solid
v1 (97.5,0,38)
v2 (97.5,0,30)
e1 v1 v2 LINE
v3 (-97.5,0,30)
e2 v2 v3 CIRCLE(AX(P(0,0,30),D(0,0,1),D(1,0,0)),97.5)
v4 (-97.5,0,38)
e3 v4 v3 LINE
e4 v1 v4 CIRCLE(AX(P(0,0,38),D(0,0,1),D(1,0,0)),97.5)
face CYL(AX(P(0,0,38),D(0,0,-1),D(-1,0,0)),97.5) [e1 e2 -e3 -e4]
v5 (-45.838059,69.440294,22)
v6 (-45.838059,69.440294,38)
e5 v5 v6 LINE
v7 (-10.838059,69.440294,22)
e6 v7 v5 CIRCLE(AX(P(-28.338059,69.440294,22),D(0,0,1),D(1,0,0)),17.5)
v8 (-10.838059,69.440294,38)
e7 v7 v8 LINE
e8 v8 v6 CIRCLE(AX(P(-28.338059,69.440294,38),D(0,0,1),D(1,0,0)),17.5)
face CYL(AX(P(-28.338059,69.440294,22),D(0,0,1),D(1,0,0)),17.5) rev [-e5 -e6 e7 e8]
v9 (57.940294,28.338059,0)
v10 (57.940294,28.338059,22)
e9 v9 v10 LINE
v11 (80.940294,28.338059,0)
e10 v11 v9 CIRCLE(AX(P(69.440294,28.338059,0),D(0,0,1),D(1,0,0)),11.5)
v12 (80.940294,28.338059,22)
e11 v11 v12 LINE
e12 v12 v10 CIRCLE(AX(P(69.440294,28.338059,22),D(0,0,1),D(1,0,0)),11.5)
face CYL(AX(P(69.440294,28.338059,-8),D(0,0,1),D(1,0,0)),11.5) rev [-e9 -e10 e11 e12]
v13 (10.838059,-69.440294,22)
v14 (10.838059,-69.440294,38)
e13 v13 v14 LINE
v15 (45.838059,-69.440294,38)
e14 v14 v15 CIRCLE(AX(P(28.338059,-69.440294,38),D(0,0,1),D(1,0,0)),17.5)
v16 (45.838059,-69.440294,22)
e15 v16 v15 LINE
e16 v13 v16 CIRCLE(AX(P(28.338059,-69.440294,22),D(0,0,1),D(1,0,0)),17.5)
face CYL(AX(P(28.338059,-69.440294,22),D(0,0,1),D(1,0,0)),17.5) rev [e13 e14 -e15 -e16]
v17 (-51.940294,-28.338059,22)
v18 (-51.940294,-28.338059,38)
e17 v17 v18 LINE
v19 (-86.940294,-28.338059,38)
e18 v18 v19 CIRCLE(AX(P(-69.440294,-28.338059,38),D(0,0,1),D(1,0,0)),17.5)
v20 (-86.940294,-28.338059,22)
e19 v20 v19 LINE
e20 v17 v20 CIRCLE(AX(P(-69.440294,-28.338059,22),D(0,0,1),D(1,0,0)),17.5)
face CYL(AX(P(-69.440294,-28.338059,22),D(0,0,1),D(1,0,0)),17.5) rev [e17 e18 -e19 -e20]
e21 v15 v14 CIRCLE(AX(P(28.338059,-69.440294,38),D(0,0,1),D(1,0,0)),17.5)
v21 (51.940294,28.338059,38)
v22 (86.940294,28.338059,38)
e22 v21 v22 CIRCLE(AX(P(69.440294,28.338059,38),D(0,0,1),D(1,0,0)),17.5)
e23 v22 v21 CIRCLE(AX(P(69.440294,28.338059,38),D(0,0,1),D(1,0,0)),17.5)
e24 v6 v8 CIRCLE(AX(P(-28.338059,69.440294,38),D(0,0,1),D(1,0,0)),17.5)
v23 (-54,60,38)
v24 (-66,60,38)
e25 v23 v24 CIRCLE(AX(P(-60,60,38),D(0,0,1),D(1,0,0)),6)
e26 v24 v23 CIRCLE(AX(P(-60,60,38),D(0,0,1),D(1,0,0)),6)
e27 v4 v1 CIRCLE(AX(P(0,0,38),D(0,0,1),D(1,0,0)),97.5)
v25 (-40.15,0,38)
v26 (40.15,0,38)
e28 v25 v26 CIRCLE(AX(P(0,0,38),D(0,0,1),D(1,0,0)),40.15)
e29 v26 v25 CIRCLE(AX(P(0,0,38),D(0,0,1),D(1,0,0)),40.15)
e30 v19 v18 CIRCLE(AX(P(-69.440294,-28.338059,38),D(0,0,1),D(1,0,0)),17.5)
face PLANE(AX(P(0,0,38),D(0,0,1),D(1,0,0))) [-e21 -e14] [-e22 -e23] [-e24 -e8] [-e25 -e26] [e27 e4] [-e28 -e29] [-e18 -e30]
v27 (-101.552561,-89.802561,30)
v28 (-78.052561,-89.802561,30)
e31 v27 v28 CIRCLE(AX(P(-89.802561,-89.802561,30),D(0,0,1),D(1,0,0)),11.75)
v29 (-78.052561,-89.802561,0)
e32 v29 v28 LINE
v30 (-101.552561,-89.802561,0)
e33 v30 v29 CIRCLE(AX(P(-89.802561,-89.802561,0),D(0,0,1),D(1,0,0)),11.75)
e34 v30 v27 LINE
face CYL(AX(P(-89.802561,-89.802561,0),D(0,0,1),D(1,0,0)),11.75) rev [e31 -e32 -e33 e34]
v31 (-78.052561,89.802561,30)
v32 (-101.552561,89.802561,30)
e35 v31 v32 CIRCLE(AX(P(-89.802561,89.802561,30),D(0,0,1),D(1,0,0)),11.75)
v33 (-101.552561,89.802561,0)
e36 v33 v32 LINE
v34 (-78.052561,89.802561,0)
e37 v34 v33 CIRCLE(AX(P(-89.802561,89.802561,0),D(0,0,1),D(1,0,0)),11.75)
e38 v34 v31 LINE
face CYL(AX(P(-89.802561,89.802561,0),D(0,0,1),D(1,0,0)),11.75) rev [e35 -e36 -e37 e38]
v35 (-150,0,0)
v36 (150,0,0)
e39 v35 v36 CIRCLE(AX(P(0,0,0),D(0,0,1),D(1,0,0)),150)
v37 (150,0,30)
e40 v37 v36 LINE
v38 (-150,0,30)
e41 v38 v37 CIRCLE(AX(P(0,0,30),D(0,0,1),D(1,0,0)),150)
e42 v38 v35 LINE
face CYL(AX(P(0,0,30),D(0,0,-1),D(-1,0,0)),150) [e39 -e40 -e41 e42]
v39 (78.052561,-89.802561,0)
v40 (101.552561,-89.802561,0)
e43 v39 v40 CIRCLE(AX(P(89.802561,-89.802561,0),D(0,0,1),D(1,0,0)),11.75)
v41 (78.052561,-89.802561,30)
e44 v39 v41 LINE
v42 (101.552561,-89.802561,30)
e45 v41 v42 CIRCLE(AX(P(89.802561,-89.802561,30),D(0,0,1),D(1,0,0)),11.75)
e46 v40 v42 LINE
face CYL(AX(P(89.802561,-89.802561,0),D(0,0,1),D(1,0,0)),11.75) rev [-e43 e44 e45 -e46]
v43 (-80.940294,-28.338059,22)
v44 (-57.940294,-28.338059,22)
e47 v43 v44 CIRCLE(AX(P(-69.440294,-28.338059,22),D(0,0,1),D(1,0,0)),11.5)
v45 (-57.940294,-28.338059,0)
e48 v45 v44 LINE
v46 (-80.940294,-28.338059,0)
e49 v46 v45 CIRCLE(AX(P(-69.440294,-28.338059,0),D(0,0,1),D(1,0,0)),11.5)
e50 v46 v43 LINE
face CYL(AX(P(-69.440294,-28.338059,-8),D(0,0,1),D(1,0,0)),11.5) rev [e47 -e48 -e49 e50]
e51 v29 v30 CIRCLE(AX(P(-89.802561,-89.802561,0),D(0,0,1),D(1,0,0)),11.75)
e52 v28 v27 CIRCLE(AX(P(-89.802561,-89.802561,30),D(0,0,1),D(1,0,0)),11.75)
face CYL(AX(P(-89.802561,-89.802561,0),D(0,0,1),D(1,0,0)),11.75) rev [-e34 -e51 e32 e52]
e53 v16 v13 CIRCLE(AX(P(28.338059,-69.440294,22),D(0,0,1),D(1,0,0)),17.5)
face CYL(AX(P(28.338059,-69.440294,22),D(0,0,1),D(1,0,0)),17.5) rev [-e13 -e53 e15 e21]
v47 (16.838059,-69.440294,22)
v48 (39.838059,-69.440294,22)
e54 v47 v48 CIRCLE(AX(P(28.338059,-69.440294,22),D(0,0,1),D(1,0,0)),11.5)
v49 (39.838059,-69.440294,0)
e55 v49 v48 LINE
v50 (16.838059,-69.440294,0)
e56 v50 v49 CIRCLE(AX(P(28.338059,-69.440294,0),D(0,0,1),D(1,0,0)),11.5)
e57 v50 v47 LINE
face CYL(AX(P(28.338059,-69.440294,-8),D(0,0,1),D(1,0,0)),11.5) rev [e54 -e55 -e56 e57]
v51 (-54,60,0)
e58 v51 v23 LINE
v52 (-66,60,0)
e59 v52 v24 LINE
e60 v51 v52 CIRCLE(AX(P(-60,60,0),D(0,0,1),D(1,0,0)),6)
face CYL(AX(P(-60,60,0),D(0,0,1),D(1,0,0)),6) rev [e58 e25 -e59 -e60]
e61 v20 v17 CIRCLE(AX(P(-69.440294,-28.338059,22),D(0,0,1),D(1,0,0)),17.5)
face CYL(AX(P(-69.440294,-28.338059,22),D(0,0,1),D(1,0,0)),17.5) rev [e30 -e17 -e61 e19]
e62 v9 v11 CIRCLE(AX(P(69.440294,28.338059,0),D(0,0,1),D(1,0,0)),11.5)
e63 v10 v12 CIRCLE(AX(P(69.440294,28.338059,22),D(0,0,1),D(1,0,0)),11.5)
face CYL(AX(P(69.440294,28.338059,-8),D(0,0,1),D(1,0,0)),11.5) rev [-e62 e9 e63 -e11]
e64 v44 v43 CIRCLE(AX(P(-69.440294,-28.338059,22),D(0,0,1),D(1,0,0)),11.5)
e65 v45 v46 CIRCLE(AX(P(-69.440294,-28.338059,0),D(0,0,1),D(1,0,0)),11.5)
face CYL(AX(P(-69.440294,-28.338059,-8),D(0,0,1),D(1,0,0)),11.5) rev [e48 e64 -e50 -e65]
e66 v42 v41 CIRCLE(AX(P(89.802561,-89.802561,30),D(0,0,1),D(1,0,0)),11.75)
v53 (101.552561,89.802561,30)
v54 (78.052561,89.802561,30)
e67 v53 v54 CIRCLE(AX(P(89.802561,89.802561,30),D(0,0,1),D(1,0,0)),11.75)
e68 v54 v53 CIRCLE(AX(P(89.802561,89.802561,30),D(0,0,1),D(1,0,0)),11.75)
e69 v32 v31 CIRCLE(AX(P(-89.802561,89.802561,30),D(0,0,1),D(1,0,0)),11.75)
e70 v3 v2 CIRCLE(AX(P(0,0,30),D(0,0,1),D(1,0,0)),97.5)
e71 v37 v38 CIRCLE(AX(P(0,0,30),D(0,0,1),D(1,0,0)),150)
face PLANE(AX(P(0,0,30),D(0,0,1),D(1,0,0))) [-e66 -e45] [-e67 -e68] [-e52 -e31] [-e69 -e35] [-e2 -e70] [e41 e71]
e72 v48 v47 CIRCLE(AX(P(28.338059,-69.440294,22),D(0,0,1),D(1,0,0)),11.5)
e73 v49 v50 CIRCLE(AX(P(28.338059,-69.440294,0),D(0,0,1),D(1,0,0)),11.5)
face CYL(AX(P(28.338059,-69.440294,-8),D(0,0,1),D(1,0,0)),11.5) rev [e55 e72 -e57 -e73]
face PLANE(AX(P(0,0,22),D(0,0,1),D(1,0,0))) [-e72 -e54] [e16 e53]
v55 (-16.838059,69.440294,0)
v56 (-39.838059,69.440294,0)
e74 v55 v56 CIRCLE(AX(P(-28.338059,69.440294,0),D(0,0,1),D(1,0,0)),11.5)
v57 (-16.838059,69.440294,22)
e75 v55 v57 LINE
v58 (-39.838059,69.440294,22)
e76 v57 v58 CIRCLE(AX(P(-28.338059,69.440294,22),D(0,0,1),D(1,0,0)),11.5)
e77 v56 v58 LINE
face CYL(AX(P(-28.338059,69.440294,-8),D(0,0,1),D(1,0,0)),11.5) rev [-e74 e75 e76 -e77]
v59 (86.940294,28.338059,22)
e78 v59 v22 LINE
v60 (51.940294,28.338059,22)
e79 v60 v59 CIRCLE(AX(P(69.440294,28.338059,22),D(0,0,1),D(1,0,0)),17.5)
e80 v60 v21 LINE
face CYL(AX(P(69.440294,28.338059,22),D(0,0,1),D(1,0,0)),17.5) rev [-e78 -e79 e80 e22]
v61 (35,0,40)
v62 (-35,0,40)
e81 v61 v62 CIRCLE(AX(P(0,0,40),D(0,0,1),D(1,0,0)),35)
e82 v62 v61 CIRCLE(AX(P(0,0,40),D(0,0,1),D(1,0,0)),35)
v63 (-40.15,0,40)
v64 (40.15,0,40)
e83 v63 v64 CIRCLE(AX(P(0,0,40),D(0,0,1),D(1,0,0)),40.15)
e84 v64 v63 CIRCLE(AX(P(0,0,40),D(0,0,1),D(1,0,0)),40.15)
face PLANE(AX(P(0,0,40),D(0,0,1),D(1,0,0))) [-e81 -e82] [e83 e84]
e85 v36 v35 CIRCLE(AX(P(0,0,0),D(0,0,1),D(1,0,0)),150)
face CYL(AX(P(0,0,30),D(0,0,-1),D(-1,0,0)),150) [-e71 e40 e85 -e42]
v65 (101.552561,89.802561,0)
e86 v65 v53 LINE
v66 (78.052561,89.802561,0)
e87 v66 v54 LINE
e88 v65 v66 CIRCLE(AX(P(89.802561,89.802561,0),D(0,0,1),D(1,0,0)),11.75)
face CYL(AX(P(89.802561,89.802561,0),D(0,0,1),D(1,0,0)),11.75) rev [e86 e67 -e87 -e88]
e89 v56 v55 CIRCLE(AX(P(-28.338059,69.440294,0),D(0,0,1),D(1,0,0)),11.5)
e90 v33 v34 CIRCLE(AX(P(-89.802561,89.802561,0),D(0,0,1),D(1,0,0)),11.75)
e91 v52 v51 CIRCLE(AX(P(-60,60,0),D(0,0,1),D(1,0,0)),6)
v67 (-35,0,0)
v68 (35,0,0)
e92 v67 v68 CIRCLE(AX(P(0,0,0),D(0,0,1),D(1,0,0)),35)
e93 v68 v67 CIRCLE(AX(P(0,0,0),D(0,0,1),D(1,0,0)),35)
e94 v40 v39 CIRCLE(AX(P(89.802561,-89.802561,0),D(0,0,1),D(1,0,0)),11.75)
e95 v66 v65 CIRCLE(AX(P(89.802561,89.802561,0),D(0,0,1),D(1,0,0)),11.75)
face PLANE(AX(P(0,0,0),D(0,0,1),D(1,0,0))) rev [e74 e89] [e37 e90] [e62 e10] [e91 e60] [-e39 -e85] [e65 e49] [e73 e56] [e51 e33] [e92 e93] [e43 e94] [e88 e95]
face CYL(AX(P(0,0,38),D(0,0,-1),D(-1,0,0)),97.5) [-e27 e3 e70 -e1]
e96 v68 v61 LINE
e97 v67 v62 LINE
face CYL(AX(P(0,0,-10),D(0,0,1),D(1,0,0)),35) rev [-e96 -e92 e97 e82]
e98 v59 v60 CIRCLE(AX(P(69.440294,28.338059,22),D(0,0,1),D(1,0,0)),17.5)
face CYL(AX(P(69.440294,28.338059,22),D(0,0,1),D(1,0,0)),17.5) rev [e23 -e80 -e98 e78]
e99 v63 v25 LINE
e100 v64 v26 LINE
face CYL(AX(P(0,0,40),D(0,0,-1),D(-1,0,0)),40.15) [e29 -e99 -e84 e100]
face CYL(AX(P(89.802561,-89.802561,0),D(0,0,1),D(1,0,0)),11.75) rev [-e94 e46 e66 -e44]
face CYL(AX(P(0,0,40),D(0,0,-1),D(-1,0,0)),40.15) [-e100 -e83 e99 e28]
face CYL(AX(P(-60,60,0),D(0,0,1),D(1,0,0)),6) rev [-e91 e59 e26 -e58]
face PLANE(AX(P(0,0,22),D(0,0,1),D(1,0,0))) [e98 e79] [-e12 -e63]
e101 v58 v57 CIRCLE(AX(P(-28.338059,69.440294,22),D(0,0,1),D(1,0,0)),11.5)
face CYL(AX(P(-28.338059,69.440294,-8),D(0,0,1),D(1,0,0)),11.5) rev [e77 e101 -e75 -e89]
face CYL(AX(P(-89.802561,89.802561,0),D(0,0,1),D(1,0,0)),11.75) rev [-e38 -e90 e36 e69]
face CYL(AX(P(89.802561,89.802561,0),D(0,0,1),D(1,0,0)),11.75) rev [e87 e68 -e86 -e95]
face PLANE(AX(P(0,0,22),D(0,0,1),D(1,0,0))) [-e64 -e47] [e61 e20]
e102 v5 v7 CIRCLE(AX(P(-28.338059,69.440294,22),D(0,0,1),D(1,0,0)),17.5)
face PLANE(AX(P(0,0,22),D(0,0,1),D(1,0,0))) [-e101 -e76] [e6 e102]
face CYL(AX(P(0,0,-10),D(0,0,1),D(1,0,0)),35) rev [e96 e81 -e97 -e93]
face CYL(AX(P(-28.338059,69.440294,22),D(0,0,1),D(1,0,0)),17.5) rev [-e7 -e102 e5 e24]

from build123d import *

# Parameters (mm, degrees)
FLANGE_DISC_PROFILE_R          = 150
FLANGE_DISC_300_DEPTH          = 30
RAISED_FACE_PROFILE_R          = 97.5
RAISED_FACE_195_DEPTH          = 8
HUB_SPIGOT_PROFILE_R           = 40.15
HUB_SPIGOT_80_3_DEPTH          = 2
THROUGH_HOLES_PROFILE_R        = 6
THROUGH_HOLES_PROFILE_R_2      = 11.75
THROUGH_HOLES_PCD254_DEPTH     = 40
COUNTERBORE_PROFILE_R          = 17.5
COUNTERBORES_4X_35_DEPTH       = 16
COUNTERBORED_HOLES_PROFILE_R   = 11.5
COUNTERBORED_HOLES_4X_23_DEPTH = 30
CENTRAL_BORE_PROFILE_R         = 35
CENTRAL_BORE_70_DEPTH          = 50


with BuildPart() as part:
    # Flange Disc Profile → Flange Disc Ø300 (new body)
    with BuildSketch(Plane.XY):
        Circle(FLANGE_DISC_PROFILE_R)
    extrude(amount=FLANGE_DISC_300_DEPTH)

    # Raised Face Profile → Raised Face Ø195 (add)
    with BuildSketch(Plane.XY.offset(30)):
        Circle(RAISED_FACE_PROFILE_R)
    extrude(amount=RAISED_FACE_195_DEPTH)

    # Hub Spigot Profile → Hub Spigot Ø80.3 (add)
    with BuildSketch(Plane.XY.offset(38)):
        Circle(HUB_SPIGOT_PROFILE_R)
    extrude(amount=HUB_SPIGOT_80_3_DEPTH)

    # Through Holes Profile → Through Holes PCD254 (cut)
    with BuildSketch(Plane.XY.offset(40)):
        with Locations((-60, 60)):
            Circle(THROUGH_HOLES_PROFILE_R)
        with Locations((89.802561211, 89.802561211)):
            Circle(THROUGH_HOLES_PROFILE_R_2)
        with Locations((89.802561211, -89.802561211)):
            Circle(THROUGH_HOLES_PROFILE_R_2)
        with Locations((-89.802561211, -89.802561211)):
            Circle(THROUGH_HOLES_PROFILE_R_2)
        with Locations((-89.802561211, 89.802561211)):
            Circle(THROUGH_HOLES_PROFILE_R_2)
    extrude(amount=-THROUGH_HOLES_PCD254_DEPTH, mode=Mode.SUBTRACT)

    # Counterbore Profile → Counterbores 4xØ35 (cut)
    with BuildSketch(Plane.XY.offset(38)):
        with Locations((-28.338059011, 69.440293861)):
            Circle(COUNTERBORE_PROFILE_R)
        with Locations((69.440293861, 28.338059011)):
            Circle(COUNTERBORE_PROFILE_R)
        with Locations((28.338059011, -69.440293861)):
            Circle(COUNTERBORE_PROFILE_R)
        with Locations((-69.440293861, -28.338059011)):
            Circle(COUNTERBORE_PROFILE_R)
    extrude(amount=-COUNTERBORES_4X_35_DEPTH, mode=Mode.SUBTRACT)

    # Counterbored Holes Profile → Counterbored Holes 4xØ23 (cut)
    with BuildSketch(Plane.XY.offset(22)):
        with Locations((-28.338059011, 69.440293861)):
            Circle(COUNTERBORED_HOLES_PROFILE_R)
        with Locations((69.440293861, 28.338059011)):
            Circle(COUNTERBORED_HOLES_PROFILE_R)
        with Locations((28.338059011, -69.440293861)):
            Circle(COUNTERBORED_HOLES_PROFILE_R)
        with Locations((-69.440293861, -28.338059011)):
            Circle(COUNTERBORED_HOLES_PROFILE_R)
    extrude(amount=-COUNTERBORED_HOLES_4X_23_DEPTH, mode=Mode.SUBTRACT)

    # Central Bore Profile → Central Bore Ø70 (cut)
    with BuildSketch(Plane.XY.offset(40)):
        Circle(CENTRAL_BORE_PROFILE_R)
    extrude(amount=-CENTRAL_BORE_70_DEPTH, mode=Mode.SUBTRACT)


solid = part.part
